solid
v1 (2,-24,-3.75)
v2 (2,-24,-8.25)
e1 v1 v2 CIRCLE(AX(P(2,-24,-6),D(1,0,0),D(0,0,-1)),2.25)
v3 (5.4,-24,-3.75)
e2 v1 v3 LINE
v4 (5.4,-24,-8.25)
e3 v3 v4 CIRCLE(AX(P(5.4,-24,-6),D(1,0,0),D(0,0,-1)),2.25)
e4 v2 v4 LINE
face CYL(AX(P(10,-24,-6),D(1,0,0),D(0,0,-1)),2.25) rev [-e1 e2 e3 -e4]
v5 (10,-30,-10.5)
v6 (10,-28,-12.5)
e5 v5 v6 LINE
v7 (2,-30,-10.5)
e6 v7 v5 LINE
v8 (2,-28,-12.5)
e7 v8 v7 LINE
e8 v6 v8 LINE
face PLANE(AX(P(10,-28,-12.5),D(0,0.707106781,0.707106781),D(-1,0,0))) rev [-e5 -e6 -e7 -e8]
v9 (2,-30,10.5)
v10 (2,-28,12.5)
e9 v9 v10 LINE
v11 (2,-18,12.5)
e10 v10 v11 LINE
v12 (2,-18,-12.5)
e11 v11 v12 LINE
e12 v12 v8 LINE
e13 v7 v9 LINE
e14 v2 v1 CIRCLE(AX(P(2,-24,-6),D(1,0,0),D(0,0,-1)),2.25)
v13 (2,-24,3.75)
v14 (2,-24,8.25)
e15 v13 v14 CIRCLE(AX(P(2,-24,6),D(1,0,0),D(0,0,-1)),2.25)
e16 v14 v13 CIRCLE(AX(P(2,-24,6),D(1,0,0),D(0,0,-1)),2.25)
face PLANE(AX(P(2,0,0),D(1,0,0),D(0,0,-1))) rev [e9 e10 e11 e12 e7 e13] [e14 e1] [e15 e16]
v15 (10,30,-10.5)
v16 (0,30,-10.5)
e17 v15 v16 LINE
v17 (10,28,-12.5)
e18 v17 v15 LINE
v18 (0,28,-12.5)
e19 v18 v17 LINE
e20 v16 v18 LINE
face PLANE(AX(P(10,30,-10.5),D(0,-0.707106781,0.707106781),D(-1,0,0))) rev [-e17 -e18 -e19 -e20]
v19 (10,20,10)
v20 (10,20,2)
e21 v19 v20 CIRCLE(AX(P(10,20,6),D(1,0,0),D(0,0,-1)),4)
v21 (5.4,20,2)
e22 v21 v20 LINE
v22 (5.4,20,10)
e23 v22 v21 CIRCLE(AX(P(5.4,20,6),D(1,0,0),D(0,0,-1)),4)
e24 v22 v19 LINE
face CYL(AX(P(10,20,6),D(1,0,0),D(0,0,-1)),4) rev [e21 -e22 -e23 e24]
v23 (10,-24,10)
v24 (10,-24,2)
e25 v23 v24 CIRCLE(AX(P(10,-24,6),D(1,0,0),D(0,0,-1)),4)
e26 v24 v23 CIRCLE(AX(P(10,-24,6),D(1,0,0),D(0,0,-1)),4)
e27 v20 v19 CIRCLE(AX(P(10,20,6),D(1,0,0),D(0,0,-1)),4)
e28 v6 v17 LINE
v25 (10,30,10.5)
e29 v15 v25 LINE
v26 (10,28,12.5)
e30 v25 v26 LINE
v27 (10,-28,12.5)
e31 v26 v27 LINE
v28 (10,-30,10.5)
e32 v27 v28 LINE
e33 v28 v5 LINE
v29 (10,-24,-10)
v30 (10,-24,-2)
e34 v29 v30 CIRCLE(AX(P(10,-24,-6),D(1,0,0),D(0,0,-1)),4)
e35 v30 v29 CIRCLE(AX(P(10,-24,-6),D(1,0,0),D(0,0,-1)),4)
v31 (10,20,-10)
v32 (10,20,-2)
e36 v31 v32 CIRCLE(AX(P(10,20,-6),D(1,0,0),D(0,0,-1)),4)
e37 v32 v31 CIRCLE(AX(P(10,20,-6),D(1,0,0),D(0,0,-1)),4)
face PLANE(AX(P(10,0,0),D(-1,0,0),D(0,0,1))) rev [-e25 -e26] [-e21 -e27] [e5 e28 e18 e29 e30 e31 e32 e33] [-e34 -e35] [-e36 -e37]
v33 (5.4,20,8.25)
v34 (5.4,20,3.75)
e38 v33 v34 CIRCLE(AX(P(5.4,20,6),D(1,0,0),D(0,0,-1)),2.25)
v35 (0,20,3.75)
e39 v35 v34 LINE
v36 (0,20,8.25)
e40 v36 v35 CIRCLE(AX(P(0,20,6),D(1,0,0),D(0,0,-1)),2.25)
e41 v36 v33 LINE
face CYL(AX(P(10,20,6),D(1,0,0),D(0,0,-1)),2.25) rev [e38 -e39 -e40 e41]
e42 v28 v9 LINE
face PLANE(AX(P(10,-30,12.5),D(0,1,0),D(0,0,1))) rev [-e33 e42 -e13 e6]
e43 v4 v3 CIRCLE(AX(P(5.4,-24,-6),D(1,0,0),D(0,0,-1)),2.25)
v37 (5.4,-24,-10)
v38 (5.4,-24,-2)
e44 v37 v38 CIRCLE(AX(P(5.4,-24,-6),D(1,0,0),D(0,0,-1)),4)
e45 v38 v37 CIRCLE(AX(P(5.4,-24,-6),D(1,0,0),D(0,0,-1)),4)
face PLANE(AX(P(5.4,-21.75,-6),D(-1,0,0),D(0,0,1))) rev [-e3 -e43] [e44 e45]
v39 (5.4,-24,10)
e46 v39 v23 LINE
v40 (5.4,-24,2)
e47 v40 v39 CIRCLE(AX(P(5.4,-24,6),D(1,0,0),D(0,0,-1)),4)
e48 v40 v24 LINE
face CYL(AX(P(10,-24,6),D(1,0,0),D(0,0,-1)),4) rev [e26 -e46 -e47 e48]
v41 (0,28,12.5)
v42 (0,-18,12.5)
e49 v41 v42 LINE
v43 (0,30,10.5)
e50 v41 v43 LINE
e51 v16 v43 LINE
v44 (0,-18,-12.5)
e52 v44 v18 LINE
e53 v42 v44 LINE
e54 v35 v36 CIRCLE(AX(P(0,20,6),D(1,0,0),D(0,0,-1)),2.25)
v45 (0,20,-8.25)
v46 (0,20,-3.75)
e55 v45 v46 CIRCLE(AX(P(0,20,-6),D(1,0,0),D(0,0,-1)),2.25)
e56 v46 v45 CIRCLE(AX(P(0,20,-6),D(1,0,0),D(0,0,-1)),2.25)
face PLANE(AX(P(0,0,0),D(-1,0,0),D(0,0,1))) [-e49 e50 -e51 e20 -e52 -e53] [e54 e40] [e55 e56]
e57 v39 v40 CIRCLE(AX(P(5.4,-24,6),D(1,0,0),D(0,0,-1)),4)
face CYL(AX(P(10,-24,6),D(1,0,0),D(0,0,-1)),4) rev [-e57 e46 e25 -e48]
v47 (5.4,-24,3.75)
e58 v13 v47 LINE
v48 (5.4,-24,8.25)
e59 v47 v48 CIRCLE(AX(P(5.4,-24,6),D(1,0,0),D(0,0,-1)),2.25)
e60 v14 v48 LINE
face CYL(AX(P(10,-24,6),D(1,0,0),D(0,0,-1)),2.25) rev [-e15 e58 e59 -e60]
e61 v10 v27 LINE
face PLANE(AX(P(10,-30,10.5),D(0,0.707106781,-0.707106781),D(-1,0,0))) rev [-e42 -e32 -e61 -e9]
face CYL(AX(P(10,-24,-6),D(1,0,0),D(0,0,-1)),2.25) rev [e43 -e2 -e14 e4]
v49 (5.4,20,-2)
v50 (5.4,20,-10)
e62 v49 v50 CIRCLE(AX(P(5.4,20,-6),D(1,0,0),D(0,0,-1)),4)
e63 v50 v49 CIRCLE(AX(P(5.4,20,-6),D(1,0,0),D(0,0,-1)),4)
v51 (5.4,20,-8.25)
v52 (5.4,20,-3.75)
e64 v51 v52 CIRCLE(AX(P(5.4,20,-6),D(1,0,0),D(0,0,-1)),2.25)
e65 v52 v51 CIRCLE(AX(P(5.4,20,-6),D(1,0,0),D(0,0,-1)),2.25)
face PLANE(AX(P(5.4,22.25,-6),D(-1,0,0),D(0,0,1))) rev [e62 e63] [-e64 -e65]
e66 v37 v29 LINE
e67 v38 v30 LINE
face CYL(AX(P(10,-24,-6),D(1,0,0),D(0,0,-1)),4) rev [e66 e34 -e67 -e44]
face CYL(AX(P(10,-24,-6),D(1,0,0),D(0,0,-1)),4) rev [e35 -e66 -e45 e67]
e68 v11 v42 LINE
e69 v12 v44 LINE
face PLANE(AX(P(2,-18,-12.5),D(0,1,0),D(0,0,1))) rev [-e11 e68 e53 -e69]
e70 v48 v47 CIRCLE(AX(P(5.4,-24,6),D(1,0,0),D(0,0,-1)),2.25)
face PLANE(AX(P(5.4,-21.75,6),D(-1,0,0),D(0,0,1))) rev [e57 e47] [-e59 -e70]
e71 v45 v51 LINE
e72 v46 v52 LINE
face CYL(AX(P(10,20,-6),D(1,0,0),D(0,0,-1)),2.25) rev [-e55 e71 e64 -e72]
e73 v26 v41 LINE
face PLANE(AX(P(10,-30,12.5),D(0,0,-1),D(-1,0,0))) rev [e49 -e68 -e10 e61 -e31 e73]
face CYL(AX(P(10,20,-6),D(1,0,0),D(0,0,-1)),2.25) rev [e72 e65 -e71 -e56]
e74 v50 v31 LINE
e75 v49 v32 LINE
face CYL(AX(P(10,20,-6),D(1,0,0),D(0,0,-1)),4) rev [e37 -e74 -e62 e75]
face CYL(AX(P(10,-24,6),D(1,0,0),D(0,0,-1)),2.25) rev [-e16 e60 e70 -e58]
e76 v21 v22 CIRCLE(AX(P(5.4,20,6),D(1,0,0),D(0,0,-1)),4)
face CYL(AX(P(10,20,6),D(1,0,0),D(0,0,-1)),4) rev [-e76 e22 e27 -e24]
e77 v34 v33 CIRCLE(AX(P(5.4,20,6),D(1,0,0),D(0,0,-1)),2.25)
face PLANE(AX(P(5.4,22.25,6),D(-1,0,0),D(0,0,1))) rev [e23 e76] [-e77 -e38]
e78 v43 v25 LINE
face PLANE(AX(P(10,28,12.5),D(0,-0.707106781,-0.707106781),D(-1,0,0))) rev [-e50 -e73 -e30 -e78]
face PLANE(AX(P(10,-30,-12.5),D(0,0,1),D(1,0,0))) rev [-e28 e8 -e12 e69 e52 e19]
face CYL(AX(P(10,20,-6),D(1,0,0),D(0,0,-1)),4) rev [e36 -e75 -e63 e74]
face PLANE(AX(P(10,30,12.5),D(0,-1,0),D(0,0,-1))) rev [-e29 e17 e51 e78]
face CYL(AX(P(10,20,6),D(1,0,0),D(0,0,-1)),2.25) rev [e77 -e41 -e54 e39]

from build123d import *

# Parameters (mm, degrees)
SKETCH1_W                                            = 25
SKETCH1_H                                            = 60
BOSS_EXTRUDE1_DEPTH                                  = 10
SKETCH4_W                                            = 25
SKETCH4_H                                            = 12
CUT_EXTRUDE3_DEPTH                                   = 2
CBORE_FOR_M4_HEXAGON_SOCKET_HEAD_CAP_SCR_D           = 4.5
CBORE_FOR_M4_HEXAGON_SOCKET_HEAD_CAP_SCR_CBORE_D     = 8
CBORE_FOR_M4_HEXAGON_SOCKET_HEAD_CAP_SCR_CBORE_DEPTH = 4.6
CBORE_FOR_M4_HEXAGON_SOCKET_HEAD_CAP_2_D             = 4.5
CBORE_FOR_M4_HEXAGON_SOCKET_HEAD_CAP_2_CBORE_D       = 8
CBORE_FOR_M4_HEXAGON_SOCKET_HEAD_CAP_2_CBORE_DEPTH   = 4.6
CHAMFER1_SIZE                                        = 2


with BuildPart() as part:
    # Sketch1 → Boss-Extrude1 (new body)
    with BuildSketch(Plane(origin=(0, 0, 0), x_dir=(0, 0, -1), z_dir=(1, 0, 0))):
        Rectangle(SKETCH1_W, SKETCH1_H)
    extrude(amount=BOSS_EXTRUDE1_DEPTH)

    # Sketch4 → Cut-Extrude3 (cut)
    with BuildSketch(Plane.ZY):
        with Locations((0, -24)):
            Rectangle(SKETCH4_W, SKETCH4_H)
    extrude(amount=-CUT_EXTRUDE3_DEPTH, mode=Mode.SUBTRACT)

    # CBORE for M4 Hexagon socket head cap scr (through all)
    with Locations(Plane(origin=(10, 0, 0), x_dir=(0, 0, -1), z_dir=(1, 0, 0))):
        with Locations((-6, -24), (6, -24)):
            CounterBoreHole(CBORE_FOR_M4_HEXAGON_SOCKET_HEAD_CAP_SCR_D / 2, CBORE_FOR_M4_HEXAGON_SOCKET_HEAD_CAP_SCR_CBORE_D / 2, CBORE_FOR_M4_HEXAGON_SOCKET_HEAD_CAP_SCR_CBORE_DEPTH)

    # CBORE for M4 Hexagon socket head cap 2 (through all)
    with Locations(Plane(origin=(10, 0, 0), x_dir=(0, 0, -1), z_dir=(1, 0, 0))):
        with Locations((6, 20), (-6, 20)):
            CounterBoreHole(CBORE_FOR_M4_HEXAGON_SOCKET_HEAD_CAP_2_D / 2, CBORE_FOR_M4_HEXAGON_SOCKET_HEAD_CAP_2_CBORE_D / 2, CBORE_FOR_M4_HEXAGON_SOCKET_HEAD_CAP_2_CBORE_DEPTH)

    # Chamfer1
    chamfer1_edges = [part.edges().sort_by_distance(p)[0] for p in [
        (6, -30, -12.5),
        (6, -30, 12.5),
        (5, 30, 12.5),
        (5, 30, -12.5),
    ]]
    chamfer(chamfer1_edges, length=CHAMFER1_SIZE)


solid = part.part
